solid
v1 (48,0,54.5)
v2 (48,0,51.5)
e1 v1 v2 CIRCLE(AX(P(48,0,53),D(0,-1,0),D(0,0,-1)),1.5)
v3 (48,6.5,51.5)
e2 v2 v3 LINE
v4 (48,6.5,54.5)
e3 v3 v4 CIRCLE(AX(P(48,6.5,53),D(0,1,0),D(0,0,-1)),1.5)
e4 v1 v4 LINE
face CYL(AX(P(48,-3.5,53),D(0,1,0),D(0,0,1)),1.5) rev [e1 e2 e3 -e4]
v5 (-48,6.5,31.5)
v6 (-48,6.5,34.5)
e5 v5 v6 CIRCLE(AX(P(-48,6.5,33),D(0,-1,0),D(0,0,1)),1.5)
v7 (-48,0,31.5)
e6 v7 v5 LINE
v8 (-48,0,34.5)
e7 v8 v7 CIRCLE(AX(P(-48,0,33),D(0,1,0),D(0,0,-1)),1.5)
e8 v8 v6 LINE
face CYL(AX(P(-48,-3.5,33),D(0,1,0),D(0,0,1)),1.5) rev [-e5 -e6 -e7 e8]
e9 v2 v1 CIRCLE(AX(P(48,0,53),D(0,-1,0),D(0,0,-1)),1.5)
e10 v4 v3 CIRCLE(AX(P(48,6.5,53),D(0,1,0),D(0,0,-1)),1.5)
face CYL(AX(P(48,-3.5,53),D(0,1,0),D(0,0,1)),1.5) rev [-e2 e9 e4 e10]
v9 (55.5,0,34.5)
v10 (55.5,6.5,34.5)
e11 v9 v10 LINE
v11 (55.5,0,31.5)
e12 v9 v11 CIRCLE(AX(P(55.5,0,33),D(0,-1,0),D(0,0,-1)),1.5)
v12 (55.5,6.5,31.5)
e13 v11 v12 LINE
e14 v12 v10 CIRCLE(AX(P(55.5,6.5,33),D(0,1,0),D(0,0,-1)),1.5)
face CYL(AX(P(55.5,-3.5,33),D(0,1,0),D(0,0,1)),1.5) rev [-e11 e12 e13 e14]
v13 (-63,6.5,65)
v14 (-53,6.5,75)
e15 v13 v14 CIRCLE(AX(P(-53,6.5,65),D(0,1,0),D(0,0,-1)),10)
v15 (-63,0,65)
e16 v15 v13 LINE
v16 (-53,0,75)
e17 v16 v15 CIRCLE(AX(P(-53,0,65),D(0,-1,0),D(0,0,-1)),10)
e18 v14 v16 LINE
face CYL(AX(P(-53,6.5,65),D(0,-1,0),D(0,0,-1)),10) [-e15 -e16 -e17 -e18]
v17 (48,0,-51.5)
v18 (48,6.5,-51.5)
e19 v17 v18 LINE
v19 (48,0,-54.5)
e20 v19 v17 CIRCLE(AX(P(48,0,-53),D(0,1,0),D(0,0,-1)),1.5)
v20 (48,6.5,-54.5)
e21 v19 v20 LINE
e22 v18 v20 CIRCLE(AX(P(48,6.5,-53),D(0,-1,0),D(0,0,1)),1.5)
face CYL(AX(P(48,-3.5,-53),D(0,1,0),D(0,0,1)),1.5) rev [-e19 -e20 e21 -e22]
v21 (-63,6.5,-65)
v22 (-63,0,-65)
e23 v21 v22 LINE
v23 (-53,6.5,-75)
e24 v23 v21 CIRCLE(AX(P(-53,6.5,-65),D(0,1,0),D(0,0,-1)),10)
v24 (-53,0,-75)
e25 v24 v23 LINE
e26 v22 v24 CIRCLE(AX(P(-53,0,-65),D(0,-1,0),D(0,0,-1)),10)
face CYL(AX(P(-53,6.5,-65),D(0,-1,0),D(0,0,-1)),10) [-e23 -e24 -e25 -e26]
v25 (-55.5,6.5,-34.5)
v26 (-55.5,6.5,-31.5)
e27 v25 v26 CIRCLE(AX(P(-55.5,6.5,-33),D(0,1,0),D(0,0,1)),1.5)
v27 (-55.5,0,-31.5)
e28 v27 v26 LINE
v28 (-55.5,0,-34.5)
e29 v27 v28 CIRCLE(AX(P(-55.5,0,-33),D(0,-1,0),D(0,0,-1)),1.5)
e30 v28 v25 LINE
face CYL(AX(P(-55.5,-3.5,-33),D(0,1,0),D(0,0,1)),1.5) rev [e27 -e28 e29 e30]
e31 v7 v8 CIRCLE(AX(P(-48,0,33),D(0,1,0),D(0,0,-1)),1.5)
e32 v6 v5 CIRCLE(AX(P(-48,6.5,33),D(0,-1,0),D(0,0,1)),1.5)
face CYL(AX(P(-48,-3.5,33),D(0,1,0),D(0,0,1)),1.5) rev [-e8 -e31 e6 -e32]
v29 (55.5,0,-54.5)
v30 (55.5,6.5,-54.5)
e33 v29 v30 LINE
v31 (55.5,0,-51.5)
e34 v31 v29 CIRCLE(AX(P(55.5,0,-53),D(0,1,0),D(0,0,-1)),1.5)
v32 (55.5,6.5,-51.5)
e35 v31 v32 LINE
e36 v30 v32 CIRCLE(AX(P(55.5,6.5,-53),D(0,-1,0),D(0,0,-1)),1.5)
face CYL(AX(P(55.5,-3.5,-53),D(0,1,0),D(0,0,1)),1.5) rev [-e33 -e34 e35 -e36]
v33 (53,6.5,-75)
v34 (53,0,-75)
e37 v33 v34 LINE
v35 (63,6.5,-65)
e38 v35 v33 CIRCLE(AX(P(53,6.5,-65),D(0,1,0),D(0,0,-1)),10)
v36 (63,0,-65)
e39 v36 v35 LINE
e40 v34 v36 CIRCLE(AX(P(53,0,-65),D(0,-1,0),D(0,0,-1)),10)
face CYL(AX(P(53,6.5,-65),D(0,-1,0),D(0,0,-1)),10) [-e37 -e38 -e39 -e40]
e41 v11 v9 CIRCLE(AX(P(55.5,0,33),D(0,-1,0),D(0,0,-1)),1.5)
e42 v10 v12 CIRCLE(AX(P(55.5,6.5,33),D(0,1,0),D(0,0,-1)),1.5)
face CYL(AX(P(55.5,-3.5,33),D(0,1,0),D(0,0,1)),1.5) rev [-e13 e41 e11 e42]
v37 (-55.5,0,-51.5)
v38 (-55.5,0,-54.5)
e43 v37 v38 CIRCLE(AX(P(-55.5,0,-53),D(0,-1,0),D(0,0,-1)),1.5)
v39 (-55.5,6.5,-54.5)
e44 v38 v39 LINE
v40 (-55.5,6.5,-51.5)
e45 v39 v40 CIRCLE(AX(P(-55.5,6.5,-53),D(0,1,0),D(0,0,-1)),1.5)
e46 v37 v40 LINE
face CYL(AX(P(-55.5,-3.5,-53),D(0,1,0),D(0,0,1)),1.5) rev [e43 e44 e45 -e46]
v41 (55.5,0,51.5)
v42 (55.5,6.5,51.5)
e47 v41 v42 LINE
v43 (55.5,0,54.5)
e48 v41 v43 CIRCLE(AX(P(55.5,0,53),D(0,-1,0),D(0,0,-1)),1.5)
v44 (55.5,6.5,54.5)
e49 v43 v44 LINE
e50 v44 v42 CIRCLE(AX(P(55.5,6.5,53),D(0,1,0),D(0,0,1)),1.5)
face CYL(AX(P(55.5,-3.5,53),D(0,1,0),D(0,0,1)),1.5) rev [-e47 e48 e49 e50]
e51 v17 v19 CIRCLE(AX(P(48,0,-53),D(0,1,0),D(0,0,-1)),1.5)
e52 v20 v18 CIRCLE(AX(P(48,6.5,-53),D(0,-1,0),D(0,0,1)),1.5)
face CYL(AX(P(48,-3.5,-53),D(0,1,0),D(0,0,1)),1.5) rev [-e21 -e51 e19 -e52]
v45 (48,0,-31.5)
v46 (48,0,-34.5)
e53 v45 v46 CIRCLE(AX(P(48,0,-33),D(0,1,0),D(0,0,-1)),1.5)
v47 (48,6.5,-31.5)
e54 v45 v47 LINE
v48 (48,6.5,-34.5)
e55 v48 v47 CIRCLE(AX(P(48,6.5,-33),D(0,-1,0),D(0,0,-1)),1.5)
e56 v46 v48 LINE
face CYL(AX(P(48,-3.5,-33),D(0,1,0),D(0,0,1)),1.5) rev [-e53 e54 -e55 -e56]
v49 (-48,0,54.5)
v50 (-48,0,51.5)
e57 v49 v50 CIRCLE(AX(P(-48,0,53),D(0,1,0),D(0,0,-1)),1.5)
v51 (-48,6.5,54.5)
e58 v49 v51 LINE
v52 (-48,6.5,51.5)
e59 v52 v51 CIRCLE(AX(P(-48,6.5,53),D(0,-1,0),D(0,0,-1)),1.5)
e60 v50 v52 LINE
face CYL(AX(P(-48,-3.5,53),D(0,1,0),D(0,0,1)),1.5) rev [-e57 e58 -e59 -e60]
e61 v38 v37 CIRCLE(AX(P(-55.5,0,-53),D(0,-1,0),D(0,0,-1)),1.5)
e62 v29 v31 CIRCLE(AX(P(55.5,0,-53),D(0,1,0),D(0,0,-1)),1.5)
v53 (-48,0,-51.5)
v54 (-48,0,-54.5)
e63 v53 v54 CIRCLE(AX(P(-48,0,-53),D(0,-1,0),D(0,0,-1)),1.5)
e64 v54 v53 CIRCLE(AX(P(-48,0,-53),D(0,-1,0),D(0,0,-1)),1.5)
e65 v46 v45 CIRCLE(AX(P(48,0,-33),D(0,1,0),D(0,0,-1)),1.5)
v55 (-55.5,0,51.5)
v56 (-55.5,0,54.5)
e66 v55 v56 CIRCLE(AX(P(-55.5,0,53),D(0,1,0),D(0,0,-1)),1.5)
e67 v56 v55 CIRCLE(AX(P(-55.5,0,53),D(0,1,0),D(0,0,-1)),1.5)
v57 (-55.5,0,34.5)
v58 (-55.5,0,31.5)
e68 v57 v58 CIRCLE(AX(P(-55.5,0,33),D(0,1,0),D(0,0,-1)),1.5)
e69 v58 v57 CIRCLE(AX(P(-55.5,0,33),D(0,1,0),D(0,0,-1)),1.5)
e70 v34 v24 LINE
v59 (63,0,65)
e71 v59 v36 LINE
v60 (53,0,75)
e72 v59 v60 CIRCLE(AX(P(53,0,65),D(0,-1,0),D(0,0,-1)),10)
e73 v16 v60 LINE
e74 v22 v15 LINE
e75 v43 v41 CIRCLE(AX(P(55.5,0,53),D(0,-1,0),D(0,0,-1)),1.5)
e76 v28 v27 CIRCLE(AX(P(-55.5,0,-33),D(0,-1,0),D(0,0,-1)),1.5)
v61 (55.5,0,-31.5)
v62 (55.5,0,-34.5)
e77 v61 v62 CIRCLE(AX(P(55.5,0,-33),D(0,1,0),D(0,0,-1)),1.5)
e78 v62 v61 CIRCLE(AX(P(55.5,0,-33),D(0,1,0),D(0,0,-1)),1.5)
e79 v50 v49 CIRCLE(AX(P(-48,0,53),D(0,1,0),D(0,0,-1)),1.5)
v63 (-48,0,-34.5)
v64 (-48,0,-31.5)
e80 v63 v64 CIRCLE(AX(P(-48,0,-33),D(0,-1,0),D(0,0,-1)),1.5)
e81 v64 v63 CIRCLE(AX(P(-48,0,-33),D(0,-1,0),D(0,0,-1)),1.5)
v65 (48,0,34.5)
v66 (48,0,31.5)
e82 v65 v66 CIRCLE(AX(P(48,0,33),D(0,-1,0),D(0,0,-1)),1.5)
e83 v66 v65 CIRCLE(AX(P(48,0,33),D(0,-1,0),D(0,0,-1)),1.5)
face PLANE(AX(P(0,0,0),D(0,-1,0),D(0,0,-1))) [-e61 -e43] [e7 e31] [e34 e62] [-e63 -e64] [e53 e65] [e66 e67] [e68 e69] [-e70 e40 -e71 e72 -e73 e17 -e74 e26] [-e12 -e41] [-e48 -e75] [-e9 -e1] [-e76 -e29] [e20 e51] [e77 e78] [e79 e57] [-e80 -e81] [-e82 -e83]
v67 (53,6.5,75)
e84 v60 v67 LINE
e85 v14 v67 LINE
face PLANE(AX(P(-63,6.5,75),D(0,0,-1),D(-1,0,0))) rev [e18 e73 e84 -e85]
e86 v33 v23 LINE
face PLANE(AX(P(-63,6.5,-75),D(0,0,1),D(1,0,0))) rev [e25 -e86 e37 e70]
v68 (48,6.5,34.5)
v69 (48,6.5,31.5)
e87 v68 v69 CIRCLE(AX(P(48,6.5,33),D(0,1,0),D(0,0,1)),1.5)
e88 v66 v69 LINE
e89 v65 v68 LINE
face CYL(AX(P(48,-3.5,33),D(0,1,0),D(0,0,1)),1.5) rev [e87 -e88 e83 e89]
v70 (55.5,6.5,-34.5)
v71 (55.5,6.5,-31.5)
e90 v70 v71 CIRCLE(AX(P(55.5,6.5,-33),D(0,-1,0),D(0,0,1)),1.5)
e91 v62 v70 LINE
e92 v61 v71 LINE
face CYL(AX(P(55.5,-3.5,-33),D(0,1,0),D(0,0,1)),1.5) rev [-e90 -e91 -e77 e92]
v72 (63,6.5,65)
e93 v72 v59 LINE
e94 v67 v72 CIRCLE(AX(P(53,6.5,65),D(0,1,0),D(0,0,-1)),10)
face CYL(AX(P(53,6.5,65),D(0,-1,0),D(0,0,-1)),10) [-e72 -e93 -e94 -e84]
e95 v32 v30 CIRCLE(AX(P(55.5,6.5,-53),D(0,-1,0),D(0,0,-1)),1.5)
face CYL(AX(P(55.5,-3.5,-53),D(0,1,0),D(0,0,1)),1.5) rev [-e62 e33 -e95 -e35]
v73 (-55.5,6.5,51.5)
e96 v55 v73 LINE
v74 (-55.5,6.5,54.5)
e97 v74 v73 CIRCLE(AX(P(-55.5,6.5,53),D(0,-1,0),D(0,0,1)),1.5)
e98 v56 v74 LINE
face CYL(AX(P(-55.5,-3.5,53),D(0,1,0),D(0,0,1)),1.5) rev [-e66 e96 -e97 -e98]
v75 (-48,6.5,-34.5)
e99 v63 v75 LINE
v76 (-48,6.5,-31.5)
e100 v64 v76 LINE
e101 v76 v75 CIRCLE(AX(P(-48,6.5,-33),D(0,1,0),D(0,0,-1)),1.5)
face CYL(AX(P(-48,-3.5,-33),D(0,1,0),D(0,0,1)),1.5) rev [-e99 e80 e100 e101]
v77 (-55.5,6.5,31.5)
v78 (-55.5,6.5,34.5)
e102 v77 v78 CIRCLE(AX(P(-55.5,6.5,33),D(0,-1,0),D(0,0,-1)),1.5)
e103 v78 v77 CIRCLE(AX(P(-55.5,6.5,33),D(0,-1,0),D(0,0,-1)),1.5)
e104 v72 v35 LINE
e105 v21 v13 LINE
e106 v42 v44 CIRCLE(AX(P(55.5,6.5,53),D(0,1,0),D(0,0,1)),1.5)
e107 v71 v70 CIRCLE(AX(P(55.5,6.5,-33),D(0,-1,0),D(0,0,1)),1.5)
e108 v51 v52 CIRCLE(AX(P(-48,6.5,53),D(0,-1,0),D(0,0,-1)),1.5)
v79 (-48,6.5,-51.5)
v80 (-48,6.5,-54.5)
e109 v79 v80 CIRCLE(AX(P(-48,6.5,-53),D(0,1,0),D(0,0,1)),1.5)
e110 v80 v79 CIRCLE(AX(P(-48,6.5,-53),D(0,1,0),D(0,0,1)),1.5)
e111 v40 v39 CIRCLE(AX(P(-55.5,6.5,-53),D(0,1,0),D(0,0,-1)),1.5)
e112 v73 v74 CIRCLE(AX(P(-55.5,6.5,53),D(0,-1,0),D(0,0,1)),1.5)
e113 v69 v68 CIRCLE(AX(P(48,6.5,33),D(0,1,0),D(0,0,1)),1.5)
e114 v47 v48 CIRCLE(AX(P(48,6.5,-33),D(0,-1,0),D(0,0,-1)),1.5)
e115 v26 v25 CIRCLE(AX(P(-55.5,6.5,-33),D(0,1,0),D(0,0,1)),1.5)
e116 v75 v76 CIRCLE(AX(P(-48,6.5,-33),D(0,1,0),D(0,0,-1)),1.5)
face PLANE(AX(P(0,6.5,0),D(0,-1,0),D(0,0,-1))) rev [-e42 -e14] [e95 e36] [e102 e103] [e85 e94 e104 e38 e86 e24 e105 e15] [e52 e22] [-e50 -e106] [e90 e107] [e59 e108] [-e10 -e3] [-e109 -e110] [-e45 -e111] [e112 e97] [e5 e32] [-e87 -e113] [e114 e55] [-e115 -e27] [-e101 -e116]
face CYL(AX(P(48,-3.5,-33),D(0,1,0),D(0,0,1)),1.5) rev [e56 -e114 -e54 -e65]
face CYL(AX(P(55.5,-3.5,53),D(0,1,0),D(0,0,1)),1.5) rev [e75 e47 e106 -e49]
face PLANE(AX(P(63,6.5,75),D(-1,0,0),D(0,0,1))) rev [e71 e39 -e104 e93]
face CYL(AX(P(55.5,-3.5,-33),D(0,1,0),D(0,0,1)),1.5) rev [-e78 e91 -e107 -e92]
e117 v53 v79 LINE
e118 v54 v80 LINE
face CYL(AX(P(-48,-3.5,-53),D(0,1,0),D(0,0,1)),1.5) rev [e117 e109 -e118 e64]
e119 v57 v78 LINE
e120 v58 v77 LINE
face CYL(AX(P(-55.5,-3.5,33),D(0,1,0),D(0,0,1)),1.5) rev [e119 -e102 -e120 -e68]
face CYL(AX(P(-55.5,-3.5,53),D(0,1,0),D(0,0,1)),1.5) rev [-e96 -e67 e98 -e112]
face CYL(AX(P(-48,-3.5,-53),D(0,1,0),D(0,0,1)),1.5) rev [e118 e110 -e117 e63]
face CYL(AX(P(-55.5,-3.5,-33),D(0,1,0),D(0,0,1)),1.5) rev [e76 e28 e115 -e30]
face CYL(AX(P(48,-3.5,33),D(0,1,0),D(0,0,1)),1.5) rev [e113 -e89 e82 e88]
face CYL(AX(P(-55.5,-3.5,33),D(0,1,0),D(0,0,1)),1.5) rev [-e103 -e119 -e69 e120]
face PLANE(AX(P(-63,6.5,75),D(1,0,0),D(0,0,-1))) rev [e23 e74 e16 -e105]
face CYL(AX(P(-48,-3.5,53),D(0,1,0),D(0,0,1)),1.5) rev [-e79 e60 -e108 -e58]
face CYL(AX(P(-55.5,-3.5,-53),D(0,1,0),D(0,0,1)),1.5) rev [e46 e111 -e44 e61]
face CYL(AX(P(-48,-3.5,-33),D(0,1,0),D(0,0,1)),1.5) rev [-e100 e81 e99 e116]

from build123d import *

# Parameters (mm, degrees)
SKETCH1_W               = 126
SKETCH1_H               = 150
BOSS_EXTRUDE1_DEPTH     = 6.5
SKETCH2_R               = 1.5
CUT_EXTRUDE1_DEPTH      = 10
MIRROR2_COPY_1_SKETCH_R = 1.5
MIRROR2_COPY_1_DEPTH    = 10
FILLET1_R               = 10


with BuildPart() as part:
    # Sketch1 → Boss-Extrude1 (new body)
    with BuildSketch(Plane(origin=(0, 0, 0), x_dir=(1, 0, 0), z_dir=(0, 1, 0))):
        Rectangle(SKETCH1_W, SKETCH1_H)
    extrude(amount=BOSS_EXTRUDE1_DEPTH)

    # Sketch2 → Cut-Extrude1 (cut)
    with BuildSketch(Plane(origin=(0, 6.5, 0), x_dir=(1, 0, 0), z_dir=(0, 1, 0))):
        with Locations(Location((-55.5, 33, 0), (0, 0, 270))):
            Circle(SKETCH2_R)
        with Locations(Location((-48, 33, 0), (0, 0, 90))):
            Circle(SKETCH2_R)
        with Locations(Location((-48, 53, 0), (0, 0, 270))):
            Circle(SKETCH2_R)
        with Locations(Location((-55.5, 53, 0), (0, 0, 90))):
            Circle(SKETCH2_R)
    cut_extrude1 = extrude(amount=-CUT_EXTRUDE1_DEPTH, mode=Mode.SUBTRACT)

    # Mirror1: Cut-Extrude1 across plane
    add(cut_extrude1.mirror(Plane(origin=(0, 0, 0), x_dir=(0, 0, 1), z_dir=(1, 0, 0))), mode=Mode.SUBTRACT)

    # Mirror2: Cut-Extrude1 across plane
    add(cut_extrude1.mirror(Plane.XY), mode=Mode.SUBTRACT)

    # Mirror2 copy 1 sketch → Mirror2 copy 1 (cut)
    with BuildSketch(Plane(origin=(0, 6.5, 0), x_dir=(-1, 0, 0), z_dir=(0, 1, 0))):
        with Locations(Location((-55.5, 33, 0), (0, 0, 270))):
            Circle(MIRROR2_COPY_1_SKETCH_R)
        with Locations(Location((-48, 33, 0), (0, 0, 90))):
            Circle(MIRROR2_COPY_1_SKETCH_R)
        with Locations(Location((-48, 53, 0), (0, 0, 270))):
            Circle(MIRROR2_COPY_1_SKETCH_R)
        with Locations(Location((-55.5, 53, 0), (0, 0, 90))):
            Circle(MIRROR2_COPY_1_SKETCH_R)
    extrude(amount=-MIRROR2_COPY_1_DEPTH, mode=Mode.SUBTRACT)

    # Fillet1
    fillet1_edges = [part.edges().sort_by_distance(p)[0] for p in [
        (63, 3.25, 75),
        (-63, 3.25, 75),
        (-63, 3.25, -75),
        (63, 3.25, -75),
    ]]
    fillet(fillet1_edges, radius=FILLET1_R)


solid = part.part
